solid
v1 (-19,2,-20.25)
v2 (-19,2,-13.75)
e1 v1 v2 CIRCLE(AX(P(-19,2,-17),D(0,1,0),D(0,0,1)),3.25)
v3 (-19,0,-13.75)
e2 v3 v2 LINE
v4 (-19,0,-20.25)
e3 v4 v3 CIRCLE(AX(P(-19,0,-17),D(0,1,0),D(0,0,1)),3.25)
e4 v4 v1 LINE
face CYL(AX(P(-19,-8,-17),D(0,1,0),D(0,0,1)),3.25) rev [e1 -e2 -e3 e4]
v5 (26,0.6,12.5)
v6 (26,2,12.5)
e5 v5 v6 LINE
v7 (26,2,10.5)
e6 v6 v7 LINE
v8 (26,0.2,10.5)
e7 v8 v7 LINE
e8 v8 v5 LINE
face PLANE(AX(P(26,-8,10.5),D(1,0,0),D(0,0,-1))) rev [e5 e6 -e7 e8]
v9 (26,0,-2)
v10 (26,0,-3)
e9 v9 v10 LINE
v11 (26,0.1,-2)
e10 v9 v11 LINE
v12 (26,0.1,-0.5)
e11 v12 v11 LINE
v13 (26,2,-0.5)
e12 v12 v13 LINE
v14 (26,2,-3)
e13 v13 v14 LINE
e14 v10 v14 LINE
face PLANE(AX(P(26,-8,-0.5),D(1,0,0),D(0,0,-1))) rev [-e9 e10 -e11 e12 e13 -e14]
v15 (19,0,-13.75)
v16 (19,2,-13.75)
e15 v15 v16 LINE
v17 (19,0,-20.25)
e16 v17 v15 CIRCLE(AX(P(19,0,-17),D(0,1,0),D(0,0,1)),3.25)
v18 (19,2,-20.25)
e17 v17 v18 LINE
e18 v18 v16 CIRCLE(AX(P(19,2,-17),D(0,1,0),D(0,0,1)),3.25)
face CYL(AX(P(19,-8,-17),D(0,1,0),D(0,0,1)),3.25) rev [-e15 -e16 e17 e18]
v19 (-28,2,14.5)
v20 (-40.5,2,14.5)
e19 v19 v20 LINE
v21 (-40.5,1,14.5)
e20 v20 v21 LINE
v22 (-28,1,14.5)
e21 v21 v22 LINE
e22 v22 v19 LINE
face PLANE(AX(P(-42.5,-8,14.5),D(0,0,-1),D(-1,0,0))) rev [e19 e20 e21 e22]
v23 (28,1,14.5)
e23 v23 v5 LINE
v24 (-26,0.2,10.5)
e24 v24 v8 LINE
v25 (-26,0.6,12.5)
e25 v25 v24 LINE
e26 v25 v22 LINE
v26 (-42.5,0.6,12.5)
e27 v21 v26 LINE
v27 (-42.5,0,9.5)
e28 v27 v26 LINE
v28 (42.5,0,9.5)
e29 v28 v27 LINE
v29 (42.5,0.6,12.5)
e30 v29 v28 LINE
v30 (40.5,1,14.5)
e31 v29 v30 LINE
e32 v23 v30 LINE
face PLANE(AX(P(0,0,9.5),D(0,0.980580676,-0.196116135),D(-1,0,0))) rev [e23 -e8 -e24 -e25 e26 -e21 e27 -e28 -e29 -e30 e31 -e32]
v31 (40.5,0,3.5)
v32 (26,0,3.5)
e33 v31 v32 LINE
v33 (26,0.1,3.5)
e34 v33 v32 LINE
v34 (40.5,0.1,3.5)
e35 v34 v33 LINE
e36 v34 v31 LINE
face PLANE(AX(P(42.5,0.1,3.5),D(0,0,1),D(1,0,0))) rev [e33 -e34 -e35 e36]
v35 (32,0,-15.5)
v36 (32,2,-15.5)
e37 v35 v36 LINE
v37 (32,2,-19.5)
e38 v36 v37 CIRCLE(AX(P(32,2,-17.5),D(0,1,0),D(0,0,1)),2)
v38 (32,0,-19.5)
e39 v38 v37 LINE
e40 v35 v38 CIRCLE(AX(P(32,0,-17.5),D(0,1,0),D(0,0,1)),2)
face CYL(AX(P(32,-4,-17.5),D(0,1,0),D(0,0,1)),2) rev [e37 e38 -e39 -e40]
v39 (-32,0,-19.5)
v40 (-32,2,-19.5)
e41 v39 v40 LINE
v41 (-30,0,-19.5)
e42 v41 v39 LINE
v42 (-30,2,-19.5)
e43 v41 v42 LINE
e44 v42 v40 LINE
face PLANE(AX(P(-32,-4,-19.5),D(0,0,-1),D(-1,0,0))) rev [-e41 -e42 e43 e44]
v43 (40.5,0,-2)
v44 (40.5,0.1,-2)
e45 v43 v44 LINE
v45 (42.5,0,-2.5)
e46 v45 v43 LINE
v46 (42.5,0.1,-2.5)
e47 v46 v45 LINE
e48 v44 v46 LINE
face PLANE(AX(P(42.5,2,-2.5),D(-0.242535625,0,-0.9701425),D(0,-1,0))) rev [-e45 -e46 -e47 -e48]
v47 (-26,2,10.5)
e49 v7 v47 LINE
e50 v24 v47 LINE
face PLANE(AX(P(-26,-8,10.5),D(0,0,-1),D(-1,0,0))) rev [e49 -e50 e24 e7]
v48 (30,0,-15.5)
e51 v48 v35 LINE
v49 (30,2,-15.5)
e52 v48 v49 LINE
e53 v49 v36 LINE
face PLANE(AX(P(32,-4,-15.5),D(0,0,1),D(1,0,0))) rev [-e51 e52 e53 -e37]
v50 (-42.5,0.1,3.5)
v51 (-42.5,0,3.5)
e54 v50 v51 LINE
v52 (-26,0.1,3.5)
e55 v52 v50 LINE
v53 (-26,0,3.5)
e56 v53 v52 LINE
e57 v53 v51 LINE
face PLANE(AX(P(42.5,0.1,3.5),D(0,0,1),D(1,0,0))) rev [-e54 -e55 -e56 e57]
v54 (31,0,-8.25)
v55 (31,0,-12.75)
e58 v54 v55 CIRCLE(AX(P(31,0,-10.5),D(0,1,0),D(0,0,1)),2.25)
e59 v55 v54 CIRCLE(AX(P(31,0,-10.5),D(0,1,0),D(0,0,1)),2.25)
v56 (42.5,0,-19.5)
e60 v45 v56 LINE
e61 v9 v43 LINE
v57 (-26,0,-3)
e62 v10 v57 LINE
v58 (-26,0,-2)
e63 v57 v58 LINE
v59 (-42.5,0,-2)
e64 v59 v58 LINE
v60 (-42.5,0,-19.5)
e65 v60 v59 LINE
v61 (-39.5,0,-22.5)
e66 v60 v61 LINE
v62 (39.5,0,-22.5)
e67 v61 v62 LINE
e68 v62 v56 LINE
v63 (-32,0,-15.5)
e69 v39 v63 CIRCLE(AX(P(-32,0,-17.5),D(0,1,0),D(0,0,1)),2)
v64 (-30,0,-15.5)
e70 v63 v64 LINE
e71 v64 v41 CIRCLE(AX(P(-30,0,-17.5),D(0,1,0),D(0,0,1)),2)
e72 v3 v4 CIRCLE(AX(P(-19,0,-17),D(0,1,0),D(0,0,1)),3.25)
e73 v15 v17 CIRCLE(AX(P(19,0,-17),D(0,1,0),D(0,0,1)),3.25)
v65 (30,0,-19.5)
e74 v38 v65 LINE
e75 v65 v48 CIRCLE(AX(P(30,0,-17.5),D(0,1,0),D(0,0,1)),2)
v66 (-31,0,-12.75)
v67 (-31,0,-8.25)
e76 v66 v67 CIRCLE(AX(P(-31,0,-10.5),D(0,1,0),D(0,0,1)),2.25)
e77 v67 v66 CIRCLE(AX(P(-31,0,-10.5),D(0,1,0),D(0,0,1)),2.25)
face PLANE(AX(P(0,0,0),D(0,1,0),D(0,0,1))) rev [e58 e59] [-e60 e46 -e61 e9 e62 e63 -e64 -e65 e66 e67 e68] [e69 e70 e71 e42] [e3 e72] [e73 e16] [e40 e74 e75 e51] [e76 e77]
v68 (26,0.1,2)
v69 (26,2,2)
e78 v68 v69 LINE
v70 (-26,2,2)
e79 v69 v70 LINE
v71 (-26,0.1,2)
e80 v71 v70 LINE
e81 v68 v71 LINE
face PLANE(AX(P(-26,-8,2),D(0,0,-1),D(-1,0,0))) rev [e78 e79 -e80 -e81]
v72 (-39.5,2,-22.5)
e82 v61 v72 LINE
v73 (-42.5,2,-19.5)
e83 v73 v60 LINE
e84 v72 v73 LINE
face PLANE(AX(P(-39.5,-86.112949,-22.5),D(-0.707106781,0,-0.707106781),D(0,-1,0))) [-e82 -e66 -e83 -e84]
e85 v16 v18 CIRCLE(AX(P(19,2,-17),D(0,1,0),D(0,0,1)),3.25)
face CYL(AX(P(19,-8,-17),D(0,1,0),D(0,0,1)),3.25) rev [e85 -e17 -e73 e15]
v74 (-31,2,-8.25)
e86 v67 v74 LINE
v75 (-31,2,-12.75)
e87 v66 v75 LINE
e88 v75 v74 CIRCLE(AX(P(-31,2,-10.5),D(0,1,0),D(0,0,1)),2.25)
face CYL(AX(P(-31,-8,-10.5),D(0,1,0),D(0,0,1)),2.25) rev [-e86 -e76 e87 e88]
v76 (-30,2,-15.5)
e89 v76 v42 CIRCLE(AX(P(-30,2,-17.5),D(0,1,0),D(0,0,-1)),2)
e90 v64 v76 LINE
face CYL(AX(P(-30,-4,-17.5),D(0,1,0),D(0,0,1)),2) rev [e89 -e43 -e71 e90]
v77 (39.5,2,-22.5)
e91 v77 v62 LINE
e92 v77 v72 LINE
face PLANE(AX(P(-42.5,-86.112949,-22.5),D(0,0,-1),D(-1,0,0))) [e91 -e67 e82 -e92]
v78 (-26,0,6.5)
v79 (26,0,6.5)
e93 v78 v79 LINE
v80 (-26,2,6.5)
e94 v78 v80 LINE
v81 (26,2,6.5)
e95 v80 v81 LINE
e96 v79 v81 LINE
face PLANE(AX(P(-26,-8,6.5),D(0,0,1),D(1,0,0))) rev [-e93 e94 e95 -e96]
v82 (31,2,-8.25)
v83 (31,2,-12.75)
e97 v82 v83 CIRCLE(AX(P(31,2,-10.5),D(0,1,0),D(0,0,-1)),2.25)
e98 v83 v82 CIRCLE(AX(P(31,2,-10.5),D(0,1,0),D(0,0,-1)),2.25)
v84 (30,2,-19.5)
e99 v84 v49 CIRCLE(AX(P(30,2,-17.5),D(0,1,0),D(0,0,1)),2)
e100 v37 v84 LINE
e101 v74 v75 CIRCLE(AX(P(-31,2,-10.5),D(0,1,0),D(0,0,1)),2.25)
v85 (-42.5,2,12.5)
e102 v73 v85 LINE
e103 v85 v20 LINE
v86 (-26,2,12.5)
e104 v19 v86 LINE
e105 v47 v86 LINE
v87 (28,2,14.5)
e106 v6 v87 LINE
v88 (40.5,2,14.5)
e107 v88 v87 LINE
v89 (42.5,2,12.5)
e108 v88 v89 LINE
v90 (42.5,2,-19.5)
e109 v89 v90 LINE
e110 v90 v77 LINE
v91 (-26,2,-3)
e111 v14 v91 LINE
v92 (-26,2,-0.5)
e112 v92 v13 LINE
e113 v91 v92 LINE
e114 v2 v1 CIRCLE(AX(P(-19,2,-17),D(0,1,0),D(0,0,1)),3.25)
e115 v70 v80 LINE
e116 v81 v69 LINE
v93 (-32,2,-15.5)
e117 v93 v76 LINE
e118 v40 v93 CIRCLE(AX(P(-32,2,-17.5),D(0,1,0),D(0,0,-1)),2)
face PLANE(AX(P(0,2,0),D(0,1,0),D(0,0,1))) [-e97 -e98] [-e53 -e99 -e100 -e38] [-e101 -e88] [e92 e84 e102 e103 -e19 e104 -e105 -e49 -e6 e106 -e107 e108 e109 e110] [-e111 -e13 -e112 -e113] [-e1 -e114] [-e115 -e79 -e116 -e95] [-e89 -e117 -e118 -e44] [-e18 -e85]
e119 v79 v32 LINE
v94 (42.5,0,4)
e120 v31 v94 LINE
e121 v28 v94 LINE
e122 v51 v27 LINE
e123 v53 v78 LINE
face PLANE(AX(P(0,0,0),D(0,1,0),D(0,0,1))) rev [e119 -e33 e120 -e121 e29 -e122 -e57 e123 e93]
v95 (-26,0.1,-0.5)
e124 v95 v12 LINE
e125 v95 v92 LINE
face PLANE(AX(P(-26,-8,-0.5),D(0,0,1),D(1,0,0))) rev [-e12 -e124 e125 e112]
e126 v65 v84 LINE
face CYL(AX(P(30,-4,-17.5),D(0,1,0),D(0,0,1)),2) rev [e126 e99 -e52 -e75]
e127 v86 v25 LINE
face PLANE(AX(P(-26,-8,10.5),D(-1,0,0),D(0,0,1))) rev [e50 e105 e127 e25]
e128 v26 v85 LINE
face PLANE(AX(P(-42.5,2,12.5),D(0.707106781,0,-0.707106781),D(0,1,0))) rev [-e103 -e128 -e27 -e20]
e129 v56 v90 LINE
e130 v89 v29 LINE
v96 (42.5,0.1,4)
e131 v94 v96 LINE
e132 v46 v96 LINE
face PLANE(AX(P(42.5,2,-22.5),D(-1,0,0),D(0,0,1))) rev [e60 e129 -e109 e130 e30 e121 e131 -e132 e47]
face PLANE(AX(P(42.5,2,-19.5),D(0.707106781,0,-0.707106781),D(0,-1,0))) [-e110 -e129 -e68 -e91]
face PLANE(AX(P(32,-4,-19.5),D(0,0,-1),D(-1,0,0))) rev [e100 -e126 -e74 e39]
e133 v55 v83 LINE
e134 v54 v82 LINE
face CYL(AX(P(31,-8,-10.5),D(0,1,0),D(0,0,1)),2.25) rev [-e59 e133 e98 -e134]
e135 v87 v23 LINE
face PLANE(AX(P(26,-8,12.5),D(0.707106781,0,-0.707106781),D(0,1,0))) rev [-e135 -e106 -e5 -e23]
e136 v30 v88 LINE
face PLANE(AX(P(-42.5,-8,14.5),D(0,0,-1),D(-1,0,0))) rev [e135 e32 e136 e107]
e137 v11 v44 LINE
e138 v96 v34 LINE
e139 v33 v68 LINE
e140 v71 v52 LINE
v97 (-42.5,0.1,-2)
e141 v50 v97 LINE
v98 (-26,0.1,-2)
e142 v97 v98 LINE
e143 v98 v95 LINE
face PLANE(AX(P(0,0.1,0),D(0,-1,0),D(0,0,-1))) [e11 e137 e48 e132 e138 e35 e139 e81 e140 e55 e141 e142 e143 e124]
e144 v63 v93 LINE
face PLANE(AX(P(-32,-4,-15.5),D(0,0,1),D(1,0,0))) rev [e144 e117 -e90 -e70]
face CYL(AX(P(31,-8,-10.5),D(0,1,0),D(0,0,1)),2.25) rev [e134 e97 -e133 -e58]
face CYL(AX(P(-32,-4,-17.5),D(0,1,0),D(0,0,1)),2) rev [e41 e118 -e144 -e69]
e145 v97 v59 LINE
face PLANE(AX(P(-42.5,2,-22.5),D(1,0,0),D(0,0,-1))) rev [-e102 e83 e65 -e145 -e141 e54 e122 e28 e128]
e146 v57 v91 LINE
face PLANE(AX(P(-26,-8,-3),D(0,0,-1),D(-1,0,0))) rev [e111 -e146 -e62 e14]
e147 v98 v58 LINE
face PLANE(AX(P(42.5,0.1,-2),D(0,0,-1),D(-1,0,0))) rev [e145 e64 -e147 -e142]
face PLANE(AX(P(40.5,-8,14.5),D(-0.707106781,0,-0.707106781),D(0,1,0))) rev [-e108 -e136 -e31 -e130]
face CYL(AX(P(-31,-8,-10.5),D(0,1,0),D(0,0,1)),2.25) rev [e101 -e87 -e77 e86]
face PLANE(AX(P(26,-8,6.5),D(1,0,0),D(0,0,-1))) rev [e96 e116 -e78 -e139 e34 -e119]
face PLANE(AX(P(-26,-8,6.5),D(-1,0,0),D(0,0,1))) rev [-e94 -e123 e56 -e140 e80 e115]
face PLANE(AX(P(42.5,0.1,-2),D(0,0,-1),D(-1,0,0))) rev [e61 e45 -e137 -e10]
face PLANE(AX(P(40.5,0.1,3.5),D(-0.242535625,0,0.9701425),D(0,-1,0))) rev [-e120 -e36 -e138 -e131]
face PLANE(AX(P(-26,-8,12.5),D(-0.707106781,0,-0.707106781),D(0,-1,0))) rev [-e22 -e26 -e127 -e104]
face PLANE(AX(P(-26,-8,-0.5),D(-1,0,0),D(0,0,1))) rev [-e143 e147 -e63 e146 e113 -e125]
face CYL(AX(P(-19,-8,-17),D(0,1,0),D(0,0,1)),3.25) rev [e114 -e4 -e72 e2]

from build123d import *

# Parameters (mm, degrees)
SKETCH1_W           = 85
SKETCH1_H           = 45
BOSS_EXTRUDE1_DEPTH = 2
SKETCH2_W           = 52
SKETCH2_H           = 12
SKETCH2_H_2         = 4.5
SKETCH2_H_3         = 2.5
SKETCH2_H_4         = 13.8
CUT_EXTRUDE1_DEPTH  = 10
SKETCH3_W           = 85
SKETCH3_H           = 13.8
CUT_EXTRUDE2_DEPTH  = 10
SKETCH5_W           = 85
SKETCH5_H           = 5.5
CUT_EXTRUDE4_DEPTH  = 0.1
CHAMFER2_SIZE       = 0.5
CHAMFER2_SIZE2      = 2
CHAMFER3_SIZE       = 2
CHAMFER3_SIZE2      = 0.5
SKETCH8_W           = 85
SKETCH8_H           = 13.8
BOSS_EXTRUDE2_DEPTH = 2
CHAMFER4_SIZE       = 3
SKETCH6_R           = 2
CUT_EXTRUDE5_DEPTH  = 10
CUT_EXTRUDE6_DEPTH  = 6
SKETCH9_R           = 3.25
CUT_EXTRUDE8_DEPTH  = 10
SKETCH4_R           = 2.25
CUT_EXTRUDE3_DEPTH  = 10
SKETCH10_W          = 85
SKETCH10_H          = 8
CUT_EXTRUDE9_DEPTH  = 10
CHAMFER5_SIZE       = 1
CHAMFER5_SIZE2      = 5
CHAMFER6_SIZE       = 2


with BuildPart() as part:
    # Sketch1 → Boss-Extrude1 (new body)
    with BuildSketch(Plane(origin=(0, 0, 0), x_dir=(1, 0, 0), z_dir=(0, 1, 0))):
        Rectangle(SKETCH1_W, SKETCH1_H)
    extrude(amount=BOSS_EXTRUDE1_DEPTH)

    # Sketch2 → Cut-Extrude1 (cut)
    with BuildSketch(Plane(origin=(0, 2, 0), x_dir=(1, 0, 0), z_dir=(0, 1, 0))):
        with Locations((0, -16.5)):
            Rectangle(SKETCH2_W, SKETCH2_H)
        with Locations((0, -4.25)):
            Rectangle(SKETCH2_W, SKETCH2_H_2)
        with Locations((0, 1.75)):
            Rectangle(SKETCH2_W, SKETCH2_H_3)
        with Locations((0, 15.6)):
            Rectangle(SKETCH2_W, SKETCH2_H_4)
    extrude(amount=-CUT_EXTRUDE1_DEPTH, mode=Mode.SUBTRACT)

    # Sketch3 → Cut-Extrude2 (cut)
    with BuildSketch(Plane(origin=(0, 2, 0), x_dir=(1, 0, 0), z_dir=(0, 1, 0))):
        with Locations((0, 15.6)):
            Rectangle(SKETCH3_W, SKETCH3_H)
    extrude(amount=-CUT_EXTRUDE2_DEPTH, mode=Mode.SUBTRACT)

    # Sketch5 → Cut-Extrude4 (cut)
    with BuildSketch(Plane.XZ):
        with Locations((0, 0.75)):
            Rectangle(SKETCH5_W, SKETCH5_H)
    extrude(amount=-CUT_EXTRUDE4_DEPTH, mode=Mode.SUBTRACT)

    # Chamfer2
    chamfer2_edges = [part.edges().sort_by_distance(p)[0] for p in [
        (42.5, 0.05, 3.5),
    ]]
    chamfer2_side = [part.faces().sort_by_distance(p)[0] for p in [
        (42.5, 1.008447858, 6.954688763),
    ]]
    chamfer(chamfer2_edges, length=CHAMFER2_SIZE, length2=CHAMFER2_SIZE2, reference=chamfer2_side[0])

    # Chamfer3
    chamfer3_edges = [part.edges().sort_by_distance(p)[0] for p in [
        (42.5, 0.05, -2),
    ]]
    chamfer3_side = [part.faces().sort_by_distance(p)[0] for p in [
        (34.25, 0.05, -2),
    ]]
    chamfer(chamfer3_edges, length=CHAMFER3_SIZE, length2=CHAMFER3_SIZE2, reference=chamfer3_side[0])

    # Sketch8 → Boss-Extrude2 (add)
    with BuildSketch(Plane(origin=(0, 2, 0), x_dir=(1, 0, 0), z_dir=(0, 1, 0))):
        with Locations((0, 15.6)):
            Rectangle(SKETCH8_W, SKETCH8_H)
    extrude(amount=-BOSS_EXTRUDE2_DEPTH)

    # Chamfer4
    chamfer4_edges = [part.edges().sort_by_distance(p)[0] for p in [
        (-42.5, 1, -22.5),
        (42.5, 1, -22.5),
    ]]
    chamfer(chamfer4_edges, length=CHAMFER4_SIZE)

    # Sketch6 → Cut-Extrude5 (cut)
    with BuildSketch(Plane(origin=(0, 2, 0), x_dir=(1, 0, 0), z_dir=(0, 1, 0))):
        with Locations(Location((-31, 17.5, 0), (0, 0, 270))):
            Circle(SKETCH6_R)
        with Locations(Location((31, 17.5, 0), (0, 0, 270))):
            Circle(SKETCH6_R)
    extrude(amount=-CUT_EXTRUDE5_DEPTH, mode=Mode.SUBTRACT)

    # Sketch7 → Cut-Extrude6 (cut)
    with BuildSketch(Plane(origin=(0, 2, 0), x_dir=(1, 0, 0), z_dir=(0, 1, 0))):
        with BuildLine():
            Line((32, 15.5), (30, 15.5))
            ThreePointArc((30, 15.5), (28, 17.5), (30, 19.5))
            Line((30, 19.5), (32, 19.5))
            ThreePointArc((32, 19.5), (34, 17.5), (32, 15.5))
        make_face()
        with BuildLine():
            Line((-32, 15.5), (-30, 15.5))
            ThreePointArc((-30, 15.5), (-28, 17.5), (-30, 19.5))
            Line((-30, 19.5), (-32, 19.5))
            ThreePointArc((-32, 19.5), (-34, 17.5), (-32, 15.5))
        make_face()
    extrude(amount=-CUT_EXTRUDE6_DEPTH, mode=Mode.SUBTRACT)

    # Sketch9 → Cut-Extrude8 (cut)
    with BuildSketch(Plane(origin=(0, 2, 0), x_dir=(1, 0, 0), z_dir=(0, 1, 0))):
        with Locations(Location((-19, 17, 0), (0, 0, 270))):
            Circle(SKETCH9_R)
        with Locations(Location((19, 17, 0), (0, 0, 270))):
            Circle(SKETCH9_R)
    extrude(amount=-CUT_EXTRUDE8_DEPTH, mode=Mode.SUBTRACT)

    # Sketch4 → Cut-Extrude3 (cut)
    with BuildSketch(Plane(origin=(0, 2, 0), x_dir=(1, 0, 0), z_dir=(0, 1, 0))):
        with Locations(Location((-31, 10.5, 0), (0, 0, 270))):
            Circle(SKETCH4_R)
        with Locations(Location((31, 10.5, 0), (0, 0, 270))):
            Circle(SKETCH4_R)
    extrude(amount=-CUT_EXTRUDE3_DEPTH, mode=Mode.SUBTRACT)

    # Sketch10 → Cut-Extrude9 (cut)
    with BuildSketch(Plane(origin=(0, 2, 0), x_dir=(1, 0, 0), z_dir=(0, 1, 0))):
        with Locations((0, -18.5)):
            Rectangle(SKETCH10_W, SKETCH10_H)
    extrude(amount=-CUT_EXTRUDE9_DEPTH, mode=Mode.SUBTRACT)

    # Chamfer5
    chamfer5_edges = [part.edges().sort_by_distance(p)[0] for p in [
        (-34.25, 0, 14.5),
    ]]
    chamfer5_side = [part.faces().sort_by_distance(p)[0] for p in [
        (-34.25, 1, 14.5),
    ]]
    chamfer(chamfer5_edges, length=CHAMFER5_SIZE, length2=CHAMFER5_SIZE2, reference=chamfer5_side[0])

    # Chamfer6
    chamfer6_edges = [part.edges().sort_by_distance(p)[0] for p in [
        (-26, 1.5, 14.5),
        (-42.5, 1.5, 14.5),
        (26, 1.5, 14.5),
        (42.5, 1.5, 14.5),
    ]]
    chamfer(chamfer6_edges, length=CHAMFER6_SIZE)


solid = part.part
